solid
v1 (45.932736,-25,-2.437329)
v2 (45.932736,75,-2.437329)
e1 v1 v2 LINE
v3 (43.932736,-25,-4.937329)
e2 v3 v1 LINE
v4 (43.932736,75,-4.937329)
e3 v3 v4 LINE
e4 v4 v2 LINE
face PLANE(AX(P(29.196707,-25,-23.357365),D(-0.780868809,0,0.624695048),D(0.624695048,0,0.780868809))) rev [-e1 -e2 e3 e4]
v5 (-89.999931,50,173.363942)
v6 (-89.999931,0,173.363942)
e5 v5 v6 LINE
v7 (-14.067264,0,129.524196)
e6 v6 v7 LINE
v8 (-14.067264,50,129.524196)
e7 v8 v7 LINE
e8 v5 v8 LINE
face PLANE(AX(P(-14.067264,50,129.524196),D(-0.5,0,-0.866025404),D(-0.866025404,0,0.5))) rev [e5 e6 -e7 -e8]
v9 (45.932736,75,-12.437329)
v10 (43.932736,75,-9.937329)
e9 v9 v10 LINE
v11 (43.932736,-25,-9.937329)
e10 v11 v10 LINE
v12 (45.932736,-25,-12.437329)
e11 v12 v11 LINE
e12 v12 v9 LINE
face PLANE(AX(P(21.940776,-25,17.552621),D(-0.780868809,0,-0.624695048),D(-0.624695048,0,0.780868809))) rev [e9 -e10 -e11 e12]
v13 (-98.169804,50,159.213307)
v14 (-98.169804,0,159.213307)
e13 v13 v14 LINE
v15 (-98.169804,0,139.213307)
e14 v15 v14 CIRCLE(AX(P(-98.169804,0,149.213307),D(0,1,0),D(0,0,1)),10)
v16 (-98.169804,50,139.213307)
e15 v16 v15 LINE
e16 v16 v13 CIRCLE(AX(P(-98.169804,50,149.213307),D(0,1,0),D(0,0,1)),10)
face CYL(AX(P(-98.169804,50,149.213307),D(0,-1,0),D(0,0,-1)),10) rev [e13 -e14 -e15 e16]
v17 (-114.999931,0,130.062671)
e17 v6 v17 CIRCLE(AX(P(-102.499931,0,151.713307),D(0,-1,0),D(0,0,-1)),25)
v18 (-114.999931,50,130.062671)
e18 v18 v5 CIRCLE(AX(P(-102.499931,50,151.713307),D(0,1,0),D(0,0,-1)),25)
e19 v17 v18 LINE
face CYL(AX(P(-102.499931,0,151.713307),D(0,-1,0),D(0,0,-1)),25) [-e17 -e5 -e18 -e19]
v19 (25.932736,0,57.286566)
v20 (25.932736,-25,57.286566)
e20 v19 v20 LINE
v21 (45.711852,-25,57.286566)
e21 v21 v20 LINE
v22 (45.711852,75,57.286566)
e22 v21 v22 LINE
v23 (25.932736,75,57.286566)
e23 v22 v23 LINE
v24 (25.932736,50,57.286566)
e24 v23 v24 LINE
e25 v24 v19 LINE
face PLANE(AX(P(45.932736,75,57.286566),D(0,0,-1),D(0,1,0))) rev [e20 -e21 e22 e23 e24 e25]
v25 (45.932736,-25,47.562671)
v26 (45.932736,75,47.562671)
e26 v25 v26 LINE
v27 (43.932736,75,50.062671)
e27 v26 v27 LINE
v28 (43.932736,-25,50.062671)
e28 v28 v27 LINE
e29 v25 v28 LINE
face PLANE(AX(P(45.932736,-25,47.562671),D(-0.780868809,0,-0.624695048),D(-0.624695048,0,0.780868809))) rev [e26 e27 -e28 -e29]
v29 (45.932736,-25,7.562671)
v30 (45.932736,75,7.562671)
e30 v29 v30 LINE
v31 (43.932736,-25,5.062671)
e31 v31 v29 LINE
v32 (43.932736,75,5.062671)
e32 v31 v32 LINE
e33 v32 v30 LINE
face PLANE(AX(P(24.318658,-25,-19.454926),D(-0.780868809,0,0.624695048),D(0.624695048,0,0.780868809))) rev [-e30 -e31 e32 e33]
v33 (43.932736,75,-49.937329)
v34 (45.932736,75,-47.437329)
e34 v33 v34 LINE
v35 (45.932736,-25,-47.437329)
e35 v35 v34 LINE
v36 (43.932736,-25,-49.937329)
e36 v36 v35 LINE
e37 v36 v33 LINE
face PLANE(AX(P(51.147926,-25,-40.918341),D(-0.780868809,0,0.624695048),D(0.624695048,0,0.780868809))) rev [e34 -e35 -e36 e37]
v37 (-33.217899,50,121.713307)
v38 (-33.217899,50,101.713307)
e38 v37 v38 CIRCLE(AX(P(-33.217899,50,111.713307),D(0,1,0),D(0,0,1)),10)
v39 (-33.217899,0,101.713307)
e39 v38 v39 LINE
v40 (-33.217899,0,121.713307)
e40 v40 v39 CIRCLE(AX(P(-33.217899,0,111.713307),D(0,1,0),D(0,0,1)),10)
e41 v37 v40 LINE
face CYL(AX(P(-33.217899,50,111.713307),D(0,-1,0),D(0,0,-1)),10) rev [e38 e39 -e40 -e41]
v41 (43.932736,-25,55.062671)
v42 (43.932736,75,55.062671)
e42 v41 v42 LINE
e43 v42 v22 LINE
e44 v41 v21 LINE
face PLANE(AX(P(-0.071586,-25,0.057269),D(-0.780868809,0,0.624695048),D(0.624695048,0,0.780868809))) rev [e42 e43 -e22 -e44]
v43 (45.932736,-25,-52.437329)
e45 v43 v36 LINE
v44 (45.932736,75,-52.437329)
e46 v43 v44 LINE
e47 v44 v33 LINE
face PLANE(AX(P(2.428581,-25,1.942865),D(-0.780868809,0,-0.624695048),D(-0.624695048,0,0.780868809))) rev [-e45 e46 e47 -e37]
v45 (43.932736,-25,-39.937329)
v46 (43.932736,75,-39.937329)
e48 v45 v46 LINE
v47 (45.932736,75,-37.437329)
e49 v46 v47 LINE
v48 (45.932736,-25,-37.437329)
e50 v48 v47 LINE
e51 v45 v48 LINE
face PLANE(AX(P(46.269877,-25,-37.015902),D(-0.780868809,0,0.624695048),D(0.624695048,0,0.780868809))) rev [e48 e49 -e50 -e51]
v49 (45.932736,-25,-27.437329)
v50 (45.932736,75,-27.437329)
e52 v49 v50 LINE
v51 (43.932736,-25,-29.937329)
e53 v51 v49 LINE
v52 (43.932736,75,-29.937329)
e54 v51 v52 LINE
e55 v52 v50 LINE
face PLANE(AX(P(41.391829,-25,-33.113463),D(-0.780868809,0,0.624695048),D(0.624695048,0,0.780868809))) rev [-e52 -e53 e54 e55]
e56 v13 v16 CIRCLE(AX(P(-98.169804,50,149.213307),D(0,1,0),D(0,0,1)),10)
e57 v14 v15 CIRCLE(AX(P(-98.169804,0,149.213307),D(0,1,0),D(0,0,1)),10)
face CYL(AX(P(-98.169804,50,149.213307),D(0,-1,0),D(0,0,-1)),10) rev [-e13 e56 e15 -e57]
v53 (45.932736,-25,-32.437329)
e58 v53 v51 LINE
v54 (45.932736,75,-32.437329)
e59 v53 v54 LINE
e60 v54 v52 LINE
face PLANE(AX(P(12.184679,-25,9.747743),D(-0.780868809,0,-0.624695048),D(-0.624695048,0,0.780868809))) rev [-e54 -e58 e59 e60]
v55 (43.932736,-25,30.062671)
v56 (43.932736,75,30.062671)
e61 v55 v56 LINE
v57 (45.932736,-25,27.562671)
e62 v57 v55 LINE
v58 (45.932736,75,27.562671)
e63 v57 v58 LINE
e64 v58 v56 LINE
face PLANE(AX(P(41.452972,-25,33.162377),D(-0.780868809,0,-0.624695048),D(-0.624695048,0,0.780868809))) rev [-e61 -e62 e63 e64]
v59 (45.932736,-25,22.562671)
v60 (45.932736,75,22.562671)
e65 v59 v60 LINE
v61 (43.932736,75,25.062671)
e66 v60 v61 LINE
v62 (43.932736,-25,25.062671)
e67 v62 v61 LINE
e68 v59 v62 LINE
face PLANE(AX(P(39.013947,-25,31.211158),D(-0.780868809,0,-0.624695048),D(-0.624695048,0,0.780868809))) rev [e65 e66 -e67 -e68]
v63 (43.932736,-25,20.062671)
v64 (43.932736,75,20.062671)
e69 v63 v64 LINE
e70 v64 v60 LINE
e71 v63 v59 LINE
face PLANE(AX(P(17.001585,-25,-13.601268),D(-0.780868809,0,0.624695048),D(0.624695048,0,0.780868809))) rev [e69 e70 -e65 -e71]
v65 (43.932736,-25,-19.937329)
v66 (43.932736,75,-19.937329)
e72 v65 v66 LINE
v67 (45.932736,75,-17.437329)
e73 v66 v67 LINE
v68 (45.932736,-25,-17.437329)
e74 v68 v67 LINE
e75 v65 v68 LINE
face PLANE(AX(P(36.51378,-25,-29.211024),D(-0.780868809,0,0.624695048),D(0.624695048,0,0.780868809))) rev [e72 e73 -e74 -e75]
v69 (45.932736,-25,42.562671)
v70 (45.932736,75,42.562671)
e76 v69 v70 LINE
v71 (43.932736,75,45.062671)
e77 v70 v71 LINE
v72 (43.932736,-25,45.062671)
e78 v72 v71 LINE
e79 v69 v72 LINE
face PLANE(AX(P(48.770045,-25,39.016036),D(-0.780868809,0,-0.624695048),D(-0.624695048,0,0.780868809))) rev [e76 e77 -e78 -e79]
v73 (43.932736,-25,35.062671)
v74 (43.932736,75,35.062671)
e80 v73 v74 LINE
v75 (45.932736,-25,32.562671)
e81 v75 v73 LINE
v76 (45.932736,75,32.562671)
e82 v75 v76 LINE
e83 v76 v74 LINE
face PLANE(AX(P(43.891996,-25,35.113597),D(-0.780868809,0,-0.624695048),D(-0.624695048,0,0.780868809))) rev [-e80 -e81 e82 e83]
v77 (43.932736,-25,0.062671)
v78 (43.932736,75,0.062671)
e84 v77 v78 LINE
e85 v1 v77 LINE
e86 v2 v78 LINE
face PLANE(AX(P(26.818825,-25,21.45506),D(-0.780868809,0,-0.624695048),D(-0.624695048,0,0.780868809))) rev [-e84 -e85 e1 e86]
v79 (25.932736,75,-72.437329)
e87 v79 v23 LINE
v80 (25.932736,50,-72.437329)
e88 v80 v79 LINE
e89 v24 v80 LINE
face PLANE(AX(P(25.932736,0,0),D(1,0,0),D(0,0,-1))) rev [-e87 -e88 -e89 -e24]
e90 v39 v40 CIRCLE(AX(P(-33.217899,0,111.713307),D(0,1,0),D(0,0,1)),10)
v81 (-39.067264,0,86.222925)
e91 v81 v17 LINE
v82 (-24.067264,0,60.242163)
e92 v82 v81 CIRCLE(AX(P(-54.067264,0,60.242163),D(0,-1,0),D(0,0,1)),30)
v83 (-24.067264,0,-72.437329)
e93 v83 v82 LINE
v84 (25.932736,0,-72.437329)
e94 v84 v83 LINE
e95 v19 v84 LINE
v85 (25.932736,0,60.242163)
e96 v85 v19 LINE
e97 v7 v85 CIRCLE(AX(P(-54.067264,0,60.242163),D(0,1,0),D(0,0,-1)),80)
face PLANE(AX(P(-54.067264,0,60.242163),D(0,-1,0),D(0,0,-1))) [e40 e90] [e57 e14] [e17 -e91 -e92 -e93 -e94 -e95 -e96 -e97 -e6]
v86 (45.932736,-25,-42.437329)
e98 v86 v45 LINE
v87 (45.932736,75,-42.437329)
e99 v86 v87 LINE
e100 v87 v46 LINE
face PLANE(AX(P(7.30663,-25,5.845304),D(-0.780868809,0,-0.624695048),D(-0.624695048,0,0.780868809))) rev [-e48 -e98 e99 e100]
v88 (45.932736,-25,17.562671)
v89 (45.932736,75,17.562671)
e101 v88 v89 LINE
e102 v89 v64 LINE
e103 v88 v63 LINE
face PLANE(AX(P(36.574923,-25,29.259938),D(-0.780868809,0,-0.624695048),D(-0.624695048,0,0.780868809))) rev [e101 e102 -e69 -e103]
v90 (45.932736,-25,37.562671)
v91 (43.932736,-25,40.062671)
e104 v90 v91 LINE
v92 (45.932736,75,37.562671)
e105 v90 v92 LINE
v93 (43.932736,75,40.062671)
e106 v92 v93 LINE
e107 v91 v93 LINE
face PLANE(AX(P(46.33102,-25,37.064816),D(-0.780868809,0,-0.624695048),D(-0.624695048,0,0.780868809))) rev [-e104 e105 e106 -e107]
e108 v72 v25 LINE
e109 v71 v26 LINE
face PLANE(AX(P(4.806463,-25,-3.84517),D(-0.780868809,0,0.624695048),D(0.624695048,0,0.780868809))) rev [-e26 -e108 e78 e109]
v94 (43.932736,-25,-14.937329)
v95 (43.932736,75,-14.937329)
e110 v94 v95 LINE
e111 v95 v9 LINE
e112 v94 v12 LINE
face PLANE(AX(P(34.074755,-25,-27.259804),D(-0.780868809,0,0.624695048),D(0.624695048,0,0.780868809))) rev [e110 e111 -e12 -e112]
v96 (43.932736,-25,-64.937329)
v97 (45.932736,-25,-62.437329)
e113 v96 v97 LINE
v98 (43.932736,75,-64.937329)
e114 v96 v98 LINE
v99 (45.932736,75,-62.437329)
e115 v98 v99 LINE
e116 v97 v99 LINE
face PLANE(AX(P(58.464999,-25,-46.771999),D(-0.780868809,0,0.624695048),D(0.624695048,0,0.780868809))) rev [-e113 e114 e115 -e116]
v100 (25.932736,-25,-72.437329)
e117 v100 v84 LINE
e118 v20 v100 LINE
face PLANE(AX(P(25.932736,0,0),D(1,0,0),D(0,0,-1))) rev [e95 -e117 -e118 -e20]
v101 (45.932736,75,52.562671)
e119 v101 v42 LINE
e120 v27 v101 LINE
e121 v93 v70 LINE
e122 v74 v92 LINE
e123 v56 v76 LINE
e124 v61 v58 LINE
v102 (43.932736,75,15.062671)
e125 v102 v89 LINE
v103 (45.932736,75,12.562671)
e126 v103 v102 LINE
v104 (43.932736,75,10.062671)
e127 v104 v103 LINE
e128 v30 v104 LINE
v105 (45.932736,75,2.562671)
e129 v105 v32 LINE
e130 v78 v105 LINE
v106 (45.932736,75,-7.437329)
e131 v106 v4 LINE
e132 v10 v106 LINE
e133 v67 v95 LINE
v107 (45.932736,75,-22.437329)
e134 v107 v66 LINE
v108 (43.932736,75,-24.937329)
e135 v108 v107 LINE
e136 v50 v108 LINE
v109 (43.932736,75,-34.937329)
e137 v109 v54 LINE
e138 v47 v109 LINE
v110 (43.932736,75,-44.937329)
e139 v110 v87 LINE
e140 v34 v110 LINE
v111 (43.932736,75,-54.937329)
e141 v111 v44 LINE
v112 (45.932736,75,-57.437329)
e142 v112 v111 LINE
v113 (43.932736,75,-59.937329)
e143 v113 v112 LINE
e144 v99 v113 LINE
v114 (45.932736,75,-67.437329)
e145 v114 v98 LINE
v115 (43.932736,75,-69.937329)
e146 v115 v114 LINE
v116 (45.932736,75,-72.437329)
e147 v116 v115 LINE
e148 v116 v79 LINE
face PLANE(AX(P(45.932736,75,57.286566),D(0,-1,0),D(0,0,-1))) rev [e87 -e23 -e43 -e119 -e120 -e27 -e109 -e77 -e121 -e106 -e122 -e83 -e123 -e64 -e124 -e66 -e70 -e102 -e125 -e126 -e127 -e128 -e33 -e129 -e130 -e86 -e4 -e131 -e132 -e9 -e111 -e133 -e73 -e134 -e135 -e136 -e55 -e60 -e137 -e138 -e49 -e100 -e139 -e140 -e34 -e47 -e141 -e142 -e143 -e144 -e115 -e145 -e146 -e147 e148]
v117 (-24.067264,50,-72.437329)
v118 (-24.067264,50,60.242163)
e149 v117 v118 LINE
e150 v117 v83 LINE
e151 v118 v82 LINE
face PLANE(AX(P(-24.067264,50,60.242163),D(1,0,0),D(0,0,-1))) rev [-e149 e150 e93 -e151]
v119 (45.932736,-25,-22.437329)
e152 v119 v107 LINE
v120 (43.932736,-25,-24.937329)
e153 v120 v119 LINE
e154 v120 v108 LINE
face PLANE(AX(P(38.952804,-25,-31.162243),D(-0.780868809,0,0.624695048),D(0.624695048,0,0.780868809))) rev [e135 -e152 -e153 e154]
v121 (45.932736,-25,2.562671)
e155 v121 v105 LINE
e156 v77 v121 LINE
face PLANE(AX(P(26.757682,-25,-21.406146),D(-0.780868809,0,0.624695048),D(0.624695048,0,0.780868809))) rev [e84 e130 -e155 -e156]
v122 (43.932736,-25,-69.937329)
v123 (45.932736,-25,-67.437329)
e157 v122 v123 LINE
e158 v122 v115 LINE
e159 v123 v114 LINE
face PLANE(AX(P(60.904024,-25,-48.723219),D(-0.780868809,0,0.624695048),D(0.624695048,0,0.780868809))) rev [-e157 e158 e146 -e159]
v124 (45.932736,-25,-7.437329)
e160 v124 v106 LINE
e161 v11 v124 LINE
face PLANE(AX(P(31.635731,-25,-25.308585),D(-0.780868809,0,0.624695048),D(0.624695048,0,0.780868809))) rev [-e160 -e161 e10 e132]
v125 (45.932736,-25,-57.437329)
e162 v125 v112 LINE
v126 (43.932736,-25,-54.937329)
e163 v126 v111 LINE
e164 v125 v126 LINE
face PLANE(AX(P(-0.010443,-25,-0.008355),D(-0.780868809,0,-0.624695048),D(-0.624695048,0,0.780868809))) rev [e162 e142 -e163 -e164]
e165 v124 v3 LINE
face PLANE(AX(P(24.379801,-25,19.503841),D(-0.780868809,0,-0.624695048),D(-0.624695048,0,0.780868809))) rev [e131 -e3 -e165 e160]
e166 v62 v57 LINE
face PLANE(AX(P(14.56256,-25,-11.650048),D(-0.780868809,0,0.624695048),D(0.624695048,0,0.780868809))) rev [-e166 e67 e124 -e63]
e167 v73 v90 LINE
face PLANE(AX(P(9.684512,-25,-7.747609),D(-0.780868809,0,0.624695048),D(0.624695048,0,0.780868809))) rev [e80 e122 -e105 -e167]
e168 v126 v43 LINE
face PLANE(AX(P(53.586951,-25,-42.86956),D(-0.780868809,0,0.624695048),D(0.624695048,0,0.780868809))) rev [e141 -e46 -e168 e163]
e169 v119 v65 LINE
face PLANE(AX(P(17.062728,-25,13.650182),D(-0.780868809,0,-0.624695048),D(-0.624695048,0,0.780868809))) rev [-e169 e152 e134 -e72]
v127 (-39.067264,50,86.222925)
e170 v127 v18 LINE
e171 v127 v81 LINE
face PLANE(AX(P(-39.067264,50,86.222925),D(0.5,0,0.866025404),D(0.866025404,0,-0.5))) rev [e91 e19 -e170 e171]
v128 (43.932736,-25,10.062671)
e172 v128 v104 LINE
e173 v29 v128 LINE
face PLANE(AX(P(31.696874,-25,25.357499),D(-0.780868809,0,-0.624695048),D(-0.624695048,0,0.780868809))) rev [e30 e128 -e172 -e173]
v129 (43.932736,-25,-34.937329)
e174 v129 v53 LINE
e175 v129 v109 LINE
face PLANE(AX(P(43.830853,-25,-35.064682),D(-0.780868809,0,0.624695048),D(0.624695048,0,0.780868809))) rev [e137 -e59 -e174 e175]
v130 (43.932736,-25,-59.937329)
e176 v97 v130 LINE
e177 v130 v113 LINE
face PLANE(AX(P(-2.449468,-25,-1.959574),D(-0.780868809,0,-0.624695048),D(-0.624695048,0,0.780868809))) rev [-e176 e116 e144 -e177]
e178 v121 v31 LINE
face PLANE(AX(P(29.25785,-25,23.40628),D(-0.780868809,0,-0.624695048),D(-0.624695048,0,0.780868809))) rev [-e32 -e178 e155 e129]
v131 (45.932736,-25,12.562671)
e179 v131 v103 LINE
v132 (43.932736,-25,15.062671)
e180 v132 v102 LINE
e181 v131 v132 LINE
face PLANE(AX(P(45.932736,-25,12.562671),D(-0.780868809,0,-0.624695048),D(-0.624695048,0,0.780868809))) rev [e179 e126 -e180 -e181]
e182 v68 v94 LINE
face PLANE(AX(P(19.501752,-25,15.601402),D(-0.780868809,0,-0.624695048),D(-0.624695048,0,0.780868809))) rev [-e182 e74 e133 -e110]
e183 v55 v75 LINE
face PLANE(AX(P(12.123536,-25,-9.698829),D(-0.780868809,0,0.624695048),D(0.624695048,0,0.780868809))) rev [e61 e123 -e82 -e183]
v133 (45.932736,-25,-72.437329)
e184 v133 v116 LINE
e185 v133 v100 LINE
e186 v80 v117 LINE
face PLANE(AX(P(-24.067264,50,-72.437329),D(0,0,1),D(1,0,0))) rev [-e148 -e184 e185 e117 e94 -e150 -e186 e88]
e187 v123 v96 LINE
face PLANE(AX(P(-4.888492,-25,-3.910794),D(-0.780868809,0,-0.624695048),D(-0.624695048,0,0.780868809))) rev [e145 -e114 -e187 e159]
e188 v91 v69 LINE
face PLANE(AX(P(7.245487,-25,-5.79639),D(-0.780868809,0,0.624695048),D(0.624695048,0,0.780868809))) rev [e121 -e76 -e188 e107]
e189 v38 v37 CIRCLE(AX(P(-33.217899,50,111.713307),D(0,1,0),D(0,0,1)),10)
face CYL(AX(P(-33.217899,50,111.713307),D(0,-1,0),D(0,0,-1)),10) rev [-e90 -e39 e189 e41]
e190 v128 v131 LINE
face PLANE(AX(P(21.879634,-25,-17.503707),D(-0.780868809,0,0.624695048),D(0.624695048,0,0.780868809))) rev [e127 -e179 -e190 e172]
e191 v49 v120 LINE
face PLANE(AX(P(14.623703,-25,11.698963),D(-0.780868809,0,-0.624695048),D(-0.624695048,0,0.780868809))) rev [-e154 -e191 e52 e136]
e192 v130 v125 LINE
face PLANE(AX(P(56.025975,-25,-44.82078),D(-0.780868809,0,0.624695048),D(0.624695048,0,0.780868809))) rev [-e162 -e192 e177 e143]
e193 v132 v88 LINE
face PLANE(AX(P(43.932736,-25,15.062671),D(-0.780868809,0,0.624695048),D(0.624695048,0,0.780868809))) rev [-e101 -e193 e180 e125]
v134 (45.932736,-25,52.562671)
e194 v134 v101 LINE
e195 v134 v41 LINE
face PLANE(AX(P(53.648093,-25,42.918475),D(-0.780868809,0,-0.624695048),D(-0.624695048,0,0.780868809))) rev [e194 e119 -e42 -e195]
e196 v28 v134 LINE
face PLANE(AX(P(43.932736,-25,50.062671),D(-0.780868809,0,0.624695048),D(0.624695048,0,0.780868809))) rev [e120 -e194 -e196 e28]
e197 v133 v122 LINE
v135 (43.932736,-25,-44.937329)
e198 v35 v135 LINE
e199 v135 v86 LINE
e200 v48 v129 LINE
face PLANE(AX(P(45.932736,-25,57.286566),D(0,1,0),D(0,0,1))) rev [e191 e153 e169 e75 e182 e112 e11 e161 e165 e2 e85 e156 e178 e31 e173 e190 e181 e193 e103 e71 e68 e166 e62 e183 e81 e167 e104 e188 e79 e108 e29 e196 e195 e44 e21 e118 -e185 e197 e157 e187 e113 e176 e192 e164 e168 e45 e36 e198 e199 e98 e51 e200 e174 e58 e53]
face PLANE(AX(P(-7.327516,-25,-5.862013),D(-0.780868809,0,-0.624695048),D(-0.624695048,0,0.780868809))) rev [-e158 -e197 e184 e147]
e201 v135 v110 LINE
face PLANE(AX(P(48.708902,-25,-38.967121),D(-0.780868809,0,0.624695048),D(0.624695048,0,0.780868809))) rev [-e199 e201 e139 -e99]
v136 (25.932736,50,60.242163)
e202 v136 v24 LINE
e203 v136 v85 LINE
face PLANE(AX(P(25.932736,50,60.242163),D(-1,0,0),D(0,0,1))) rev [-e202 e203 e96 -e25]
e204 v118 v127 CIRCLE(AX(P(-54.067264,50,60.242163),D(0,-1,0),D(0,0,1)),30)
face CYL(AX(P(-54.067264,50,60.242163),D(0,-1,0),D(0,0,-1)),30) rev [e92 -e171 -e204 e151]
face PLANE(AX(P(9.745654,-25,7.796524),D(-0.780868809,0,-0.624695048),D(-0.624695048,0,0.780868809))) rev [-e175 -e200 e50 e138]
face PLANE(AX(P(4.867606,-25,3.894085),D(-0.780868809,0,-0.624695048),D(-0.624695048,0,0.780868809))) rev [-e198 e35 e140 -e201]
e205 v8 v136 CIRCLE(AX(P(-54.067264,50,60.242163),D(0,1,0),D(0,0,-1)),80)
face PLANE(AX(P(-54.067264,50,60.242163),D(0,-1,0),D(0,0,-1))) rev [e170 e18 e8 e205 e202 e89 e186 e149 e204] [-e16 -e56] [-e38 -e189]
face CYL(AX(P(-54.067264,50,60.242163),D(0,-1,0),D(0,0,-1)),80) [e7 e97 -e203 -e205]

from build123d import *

# Parameters (mm, degrees)
SKETCH1_R           = 10
BOSS_EXTRUDE1_DEPTH = 50
FILLET1_RADIUS      = 25
FILLET1_LENGTH      = 50
SKETCH2_W           = 129.723894377
SKETCH2_H           = 100
BOSS_EXTRUDE2_DEPTH = 20
CUT_EXTRUDE1_DEPTH  = 240.757846963


with BuildPart() as part:
    # Sketch1 → Boss-Extrude1 (new body)
    with BuildSketch(Plane(origin=(0, 0, 0), x_dir=(1, 0, 0), z_dir=(0, 1, 0))):
        with BuildLine():
            Line((-39.067263876, -86.222925476), (-136.650566368, -142.562671438))
            Line((-136.650566368, -142.562671438), (-111.650566368, -185.863941628))
            Line((-111.650566368, -185.863941628), (-14.067263876, -129.524195665))
            ThreePointArc((-14.067263876, -129.524195665), (15.214768427, -100.242163363), (25.932736124, -60.242163363))
            Line((25.932736124, -60.242163363), (25.932736124, 72.437328562))
            Line((25.932736124, 72.437328562), (-24.067263876, 72.437328562))
            Line((-24.067263876, 72.437328562), (-24.067263876, -60.242163363))
            ThreePointArc((-24.067263876, -60.242163363), (-28.086501763, -75.242163363), (-39.067263876, -86.222925476))
        make_face()
        with Locations(Location((-98.169804255, -149.213306533, 0), (0, 0, 270))):
            Circle(SKETCH1_R, mode=Mode.SUBTRACT)
        with Locations(Location((-33.217898971, -111.713306533, 0), (0, 0, 270))):
            Circle(SKETCH1_R, mode=Mode.SUBTRACT)
    extrude(amount=BOSS_EXTRUDE1_DEPTH)

    # Fillet1: full round fillet: the end face becomes a half cylinder, R = half its width
    fillet1_face = Plane((-124.150566368, 25, 164.213306533), x_dir=(0, 1, 0), z_dir=(-0.866025403784, 0, 0.5))  # on the end face: x along it, z out of the body
    fillet1_slab = fillet1_face.offset(-FILLET1_RADIUS / 2) * Box(FILLET1_LENGTH, 2 * FILLET1_RADIUS, FILLET1_RADIUS, mode=Mode.PRIVATE)  # the body's end, R deep
    fillet1_round = Plane((-102.499931273, 25, 151.713306533), x_dir=(-0.866025403784, 0, 0.5), z_dir=(0, 1, 0)) * Cylinder(FILLET1_RADIUS, FILLET1_LENGTH, mode=Mode.PRIVATE)  # its axis R under the face
    add(fillet1_slab - fillet1_round, mode=Mode.SUBTRACT)

    # Sketch2 → Boss-Extrude2 (add)
    with BuildSketch(Plane(origin=(25.932736124, 0, 0), x_dir=(0, 0, -1), z_dir=(1, 0, 0))):
        with Locations((7.575381374, 25)):
            Rectangle(SKETCH2_W, SKETCH2_H)
    extrude(amount=BOSS_EXTRUDE2_DEPTH)

    # Sketch3 → Cut-Extrude1 (cut, through all)
    with BuildSketch(Plane(origin=(0, 75, 0), x_dir=(1, 0, 0), z_dir=(0, 1, 0))):
        Polygon((45.932736124, 67.437328562), (45.932736124, 72.437328562), (43.932736124, 69.937328562), align=None)
        Polygon((45.932736124, 62.437328562), (45.932736124, 67.437328562), (43.932736124, 64.937328562), align=None)
        Polygon((45.932736124, 57.437328562), (45.932736124, 62.437328562), (43.932736124, 59.937328562), align=None)
        Polygon((45.932736124, 52.437328562), (45.932736124, 57.437328562), (43.932736124, 54.937328562), align=None)
        Polygon((45.932736124, 47.437328562), (45.932736124, 52.437328562), (43.932736124, 49.937328562), align=None)
        Polygon((45.932736124, 42.437328562), (45.932736124, 47.437328562), (43.932736124, 44.937328562), align=None)
        Polygon((45.932736124, 37.437328562), (45.932736124, 42.437328562), (43.932736124, 39.937328562), align=None)
        Polygon((45.932736124, 32.437328562), (45.932736124, 37.437328562), (43.932736124, 34.937328562), align=None)
        Polygon((45.932736124, 27.437328562), (45.932736124, 32.437328562), (43.932736124, 29.937328562), align=None)
        Polygon((45.932736124, 22.437328562), (45.932736124, 27.437328562), (43.932736124, 24.937328562), align=None)
        Polygon((45.932736124, 17.437328562), (45.932736124, 22.437328562), (43.932736124, 19.937328562), align=None)
        Polygon((45.932736124, 12.437328562), (45.932736124, 17.437328562), (43.932736124, 14.937328562), align=None)
        Polygon((45.932736124, 7.437328562), (45.932736124, 12.437328562), (43.932736124, 9.937328562), align=None)
        Polygon((45.932736124, 2.437328562), (45.932736124, 7.437328562), (43.932736124, 4.937328562), align=None)
        Polygon((45.932736124, -2.562671438), (45.932736124, 2.437328562), (43.932736124, -0.062671438), align=None)
        Polygon((45.932736124, -7.562671438), (45.932736124, -2.562671438), (43.932736124, -5.062671438), align=None)
        Polygon((45.932736124, -12.562671438), (45.932736124, -7.562671438), (43.932736124, -10.062671438), align=None)
        Polygon((45.932736124, -22.562671438), (45.932736124, -17.562671438), (43.932736124, -20.062671438), align=None)
        Polygon((45.932736124, -27.562671438), (45.932736124, -22.562671438), (43.932736124, -25.062671438), align=None)
        Polygon((45.932736124, -32.562671438), (45.932736124, -27.562671438), (43.932736124, -30.062671438), align=None)
        Polygon((45.932736124, -37.562671438), (45.932736124, -32.562671438), (43.932736124, -35.062671438), align=None)
        Polygon((45.932736124, -42.562671438), (45.932736124, -37.562671438), (43.932736124, -40.062671438), align=None)
        Polygon((45.932736124, -47.562671438), (45.932736124, -42.562671438), (43.932736124, -45.062671438), align=None)
        Polygon((45.932736124, -57.286565815), (45.932736124, -52.562671438), (43.932736124, -55.062671438), (45.711851625, -57.286565815), align=None)
        Polygon((45.932736124, -57.562671438), (45.932736124, -62.562671438), (43.932736124, -60.062671438), align=None)
        Polygon((45.932736124, -12.562671438), (45.932736124, -17.562671438), (43.932736124, -15.062671438), align=None)
        Polygon((45.932736124, -47.562671438), (45.932736124, -52.562671438), (43.932736124, -50.062671438), align=None)
    extrude(amount=-CUT_EXTRUDE1_DEPTH, mode=Mode.SUBTRACT)


solid = part.part
